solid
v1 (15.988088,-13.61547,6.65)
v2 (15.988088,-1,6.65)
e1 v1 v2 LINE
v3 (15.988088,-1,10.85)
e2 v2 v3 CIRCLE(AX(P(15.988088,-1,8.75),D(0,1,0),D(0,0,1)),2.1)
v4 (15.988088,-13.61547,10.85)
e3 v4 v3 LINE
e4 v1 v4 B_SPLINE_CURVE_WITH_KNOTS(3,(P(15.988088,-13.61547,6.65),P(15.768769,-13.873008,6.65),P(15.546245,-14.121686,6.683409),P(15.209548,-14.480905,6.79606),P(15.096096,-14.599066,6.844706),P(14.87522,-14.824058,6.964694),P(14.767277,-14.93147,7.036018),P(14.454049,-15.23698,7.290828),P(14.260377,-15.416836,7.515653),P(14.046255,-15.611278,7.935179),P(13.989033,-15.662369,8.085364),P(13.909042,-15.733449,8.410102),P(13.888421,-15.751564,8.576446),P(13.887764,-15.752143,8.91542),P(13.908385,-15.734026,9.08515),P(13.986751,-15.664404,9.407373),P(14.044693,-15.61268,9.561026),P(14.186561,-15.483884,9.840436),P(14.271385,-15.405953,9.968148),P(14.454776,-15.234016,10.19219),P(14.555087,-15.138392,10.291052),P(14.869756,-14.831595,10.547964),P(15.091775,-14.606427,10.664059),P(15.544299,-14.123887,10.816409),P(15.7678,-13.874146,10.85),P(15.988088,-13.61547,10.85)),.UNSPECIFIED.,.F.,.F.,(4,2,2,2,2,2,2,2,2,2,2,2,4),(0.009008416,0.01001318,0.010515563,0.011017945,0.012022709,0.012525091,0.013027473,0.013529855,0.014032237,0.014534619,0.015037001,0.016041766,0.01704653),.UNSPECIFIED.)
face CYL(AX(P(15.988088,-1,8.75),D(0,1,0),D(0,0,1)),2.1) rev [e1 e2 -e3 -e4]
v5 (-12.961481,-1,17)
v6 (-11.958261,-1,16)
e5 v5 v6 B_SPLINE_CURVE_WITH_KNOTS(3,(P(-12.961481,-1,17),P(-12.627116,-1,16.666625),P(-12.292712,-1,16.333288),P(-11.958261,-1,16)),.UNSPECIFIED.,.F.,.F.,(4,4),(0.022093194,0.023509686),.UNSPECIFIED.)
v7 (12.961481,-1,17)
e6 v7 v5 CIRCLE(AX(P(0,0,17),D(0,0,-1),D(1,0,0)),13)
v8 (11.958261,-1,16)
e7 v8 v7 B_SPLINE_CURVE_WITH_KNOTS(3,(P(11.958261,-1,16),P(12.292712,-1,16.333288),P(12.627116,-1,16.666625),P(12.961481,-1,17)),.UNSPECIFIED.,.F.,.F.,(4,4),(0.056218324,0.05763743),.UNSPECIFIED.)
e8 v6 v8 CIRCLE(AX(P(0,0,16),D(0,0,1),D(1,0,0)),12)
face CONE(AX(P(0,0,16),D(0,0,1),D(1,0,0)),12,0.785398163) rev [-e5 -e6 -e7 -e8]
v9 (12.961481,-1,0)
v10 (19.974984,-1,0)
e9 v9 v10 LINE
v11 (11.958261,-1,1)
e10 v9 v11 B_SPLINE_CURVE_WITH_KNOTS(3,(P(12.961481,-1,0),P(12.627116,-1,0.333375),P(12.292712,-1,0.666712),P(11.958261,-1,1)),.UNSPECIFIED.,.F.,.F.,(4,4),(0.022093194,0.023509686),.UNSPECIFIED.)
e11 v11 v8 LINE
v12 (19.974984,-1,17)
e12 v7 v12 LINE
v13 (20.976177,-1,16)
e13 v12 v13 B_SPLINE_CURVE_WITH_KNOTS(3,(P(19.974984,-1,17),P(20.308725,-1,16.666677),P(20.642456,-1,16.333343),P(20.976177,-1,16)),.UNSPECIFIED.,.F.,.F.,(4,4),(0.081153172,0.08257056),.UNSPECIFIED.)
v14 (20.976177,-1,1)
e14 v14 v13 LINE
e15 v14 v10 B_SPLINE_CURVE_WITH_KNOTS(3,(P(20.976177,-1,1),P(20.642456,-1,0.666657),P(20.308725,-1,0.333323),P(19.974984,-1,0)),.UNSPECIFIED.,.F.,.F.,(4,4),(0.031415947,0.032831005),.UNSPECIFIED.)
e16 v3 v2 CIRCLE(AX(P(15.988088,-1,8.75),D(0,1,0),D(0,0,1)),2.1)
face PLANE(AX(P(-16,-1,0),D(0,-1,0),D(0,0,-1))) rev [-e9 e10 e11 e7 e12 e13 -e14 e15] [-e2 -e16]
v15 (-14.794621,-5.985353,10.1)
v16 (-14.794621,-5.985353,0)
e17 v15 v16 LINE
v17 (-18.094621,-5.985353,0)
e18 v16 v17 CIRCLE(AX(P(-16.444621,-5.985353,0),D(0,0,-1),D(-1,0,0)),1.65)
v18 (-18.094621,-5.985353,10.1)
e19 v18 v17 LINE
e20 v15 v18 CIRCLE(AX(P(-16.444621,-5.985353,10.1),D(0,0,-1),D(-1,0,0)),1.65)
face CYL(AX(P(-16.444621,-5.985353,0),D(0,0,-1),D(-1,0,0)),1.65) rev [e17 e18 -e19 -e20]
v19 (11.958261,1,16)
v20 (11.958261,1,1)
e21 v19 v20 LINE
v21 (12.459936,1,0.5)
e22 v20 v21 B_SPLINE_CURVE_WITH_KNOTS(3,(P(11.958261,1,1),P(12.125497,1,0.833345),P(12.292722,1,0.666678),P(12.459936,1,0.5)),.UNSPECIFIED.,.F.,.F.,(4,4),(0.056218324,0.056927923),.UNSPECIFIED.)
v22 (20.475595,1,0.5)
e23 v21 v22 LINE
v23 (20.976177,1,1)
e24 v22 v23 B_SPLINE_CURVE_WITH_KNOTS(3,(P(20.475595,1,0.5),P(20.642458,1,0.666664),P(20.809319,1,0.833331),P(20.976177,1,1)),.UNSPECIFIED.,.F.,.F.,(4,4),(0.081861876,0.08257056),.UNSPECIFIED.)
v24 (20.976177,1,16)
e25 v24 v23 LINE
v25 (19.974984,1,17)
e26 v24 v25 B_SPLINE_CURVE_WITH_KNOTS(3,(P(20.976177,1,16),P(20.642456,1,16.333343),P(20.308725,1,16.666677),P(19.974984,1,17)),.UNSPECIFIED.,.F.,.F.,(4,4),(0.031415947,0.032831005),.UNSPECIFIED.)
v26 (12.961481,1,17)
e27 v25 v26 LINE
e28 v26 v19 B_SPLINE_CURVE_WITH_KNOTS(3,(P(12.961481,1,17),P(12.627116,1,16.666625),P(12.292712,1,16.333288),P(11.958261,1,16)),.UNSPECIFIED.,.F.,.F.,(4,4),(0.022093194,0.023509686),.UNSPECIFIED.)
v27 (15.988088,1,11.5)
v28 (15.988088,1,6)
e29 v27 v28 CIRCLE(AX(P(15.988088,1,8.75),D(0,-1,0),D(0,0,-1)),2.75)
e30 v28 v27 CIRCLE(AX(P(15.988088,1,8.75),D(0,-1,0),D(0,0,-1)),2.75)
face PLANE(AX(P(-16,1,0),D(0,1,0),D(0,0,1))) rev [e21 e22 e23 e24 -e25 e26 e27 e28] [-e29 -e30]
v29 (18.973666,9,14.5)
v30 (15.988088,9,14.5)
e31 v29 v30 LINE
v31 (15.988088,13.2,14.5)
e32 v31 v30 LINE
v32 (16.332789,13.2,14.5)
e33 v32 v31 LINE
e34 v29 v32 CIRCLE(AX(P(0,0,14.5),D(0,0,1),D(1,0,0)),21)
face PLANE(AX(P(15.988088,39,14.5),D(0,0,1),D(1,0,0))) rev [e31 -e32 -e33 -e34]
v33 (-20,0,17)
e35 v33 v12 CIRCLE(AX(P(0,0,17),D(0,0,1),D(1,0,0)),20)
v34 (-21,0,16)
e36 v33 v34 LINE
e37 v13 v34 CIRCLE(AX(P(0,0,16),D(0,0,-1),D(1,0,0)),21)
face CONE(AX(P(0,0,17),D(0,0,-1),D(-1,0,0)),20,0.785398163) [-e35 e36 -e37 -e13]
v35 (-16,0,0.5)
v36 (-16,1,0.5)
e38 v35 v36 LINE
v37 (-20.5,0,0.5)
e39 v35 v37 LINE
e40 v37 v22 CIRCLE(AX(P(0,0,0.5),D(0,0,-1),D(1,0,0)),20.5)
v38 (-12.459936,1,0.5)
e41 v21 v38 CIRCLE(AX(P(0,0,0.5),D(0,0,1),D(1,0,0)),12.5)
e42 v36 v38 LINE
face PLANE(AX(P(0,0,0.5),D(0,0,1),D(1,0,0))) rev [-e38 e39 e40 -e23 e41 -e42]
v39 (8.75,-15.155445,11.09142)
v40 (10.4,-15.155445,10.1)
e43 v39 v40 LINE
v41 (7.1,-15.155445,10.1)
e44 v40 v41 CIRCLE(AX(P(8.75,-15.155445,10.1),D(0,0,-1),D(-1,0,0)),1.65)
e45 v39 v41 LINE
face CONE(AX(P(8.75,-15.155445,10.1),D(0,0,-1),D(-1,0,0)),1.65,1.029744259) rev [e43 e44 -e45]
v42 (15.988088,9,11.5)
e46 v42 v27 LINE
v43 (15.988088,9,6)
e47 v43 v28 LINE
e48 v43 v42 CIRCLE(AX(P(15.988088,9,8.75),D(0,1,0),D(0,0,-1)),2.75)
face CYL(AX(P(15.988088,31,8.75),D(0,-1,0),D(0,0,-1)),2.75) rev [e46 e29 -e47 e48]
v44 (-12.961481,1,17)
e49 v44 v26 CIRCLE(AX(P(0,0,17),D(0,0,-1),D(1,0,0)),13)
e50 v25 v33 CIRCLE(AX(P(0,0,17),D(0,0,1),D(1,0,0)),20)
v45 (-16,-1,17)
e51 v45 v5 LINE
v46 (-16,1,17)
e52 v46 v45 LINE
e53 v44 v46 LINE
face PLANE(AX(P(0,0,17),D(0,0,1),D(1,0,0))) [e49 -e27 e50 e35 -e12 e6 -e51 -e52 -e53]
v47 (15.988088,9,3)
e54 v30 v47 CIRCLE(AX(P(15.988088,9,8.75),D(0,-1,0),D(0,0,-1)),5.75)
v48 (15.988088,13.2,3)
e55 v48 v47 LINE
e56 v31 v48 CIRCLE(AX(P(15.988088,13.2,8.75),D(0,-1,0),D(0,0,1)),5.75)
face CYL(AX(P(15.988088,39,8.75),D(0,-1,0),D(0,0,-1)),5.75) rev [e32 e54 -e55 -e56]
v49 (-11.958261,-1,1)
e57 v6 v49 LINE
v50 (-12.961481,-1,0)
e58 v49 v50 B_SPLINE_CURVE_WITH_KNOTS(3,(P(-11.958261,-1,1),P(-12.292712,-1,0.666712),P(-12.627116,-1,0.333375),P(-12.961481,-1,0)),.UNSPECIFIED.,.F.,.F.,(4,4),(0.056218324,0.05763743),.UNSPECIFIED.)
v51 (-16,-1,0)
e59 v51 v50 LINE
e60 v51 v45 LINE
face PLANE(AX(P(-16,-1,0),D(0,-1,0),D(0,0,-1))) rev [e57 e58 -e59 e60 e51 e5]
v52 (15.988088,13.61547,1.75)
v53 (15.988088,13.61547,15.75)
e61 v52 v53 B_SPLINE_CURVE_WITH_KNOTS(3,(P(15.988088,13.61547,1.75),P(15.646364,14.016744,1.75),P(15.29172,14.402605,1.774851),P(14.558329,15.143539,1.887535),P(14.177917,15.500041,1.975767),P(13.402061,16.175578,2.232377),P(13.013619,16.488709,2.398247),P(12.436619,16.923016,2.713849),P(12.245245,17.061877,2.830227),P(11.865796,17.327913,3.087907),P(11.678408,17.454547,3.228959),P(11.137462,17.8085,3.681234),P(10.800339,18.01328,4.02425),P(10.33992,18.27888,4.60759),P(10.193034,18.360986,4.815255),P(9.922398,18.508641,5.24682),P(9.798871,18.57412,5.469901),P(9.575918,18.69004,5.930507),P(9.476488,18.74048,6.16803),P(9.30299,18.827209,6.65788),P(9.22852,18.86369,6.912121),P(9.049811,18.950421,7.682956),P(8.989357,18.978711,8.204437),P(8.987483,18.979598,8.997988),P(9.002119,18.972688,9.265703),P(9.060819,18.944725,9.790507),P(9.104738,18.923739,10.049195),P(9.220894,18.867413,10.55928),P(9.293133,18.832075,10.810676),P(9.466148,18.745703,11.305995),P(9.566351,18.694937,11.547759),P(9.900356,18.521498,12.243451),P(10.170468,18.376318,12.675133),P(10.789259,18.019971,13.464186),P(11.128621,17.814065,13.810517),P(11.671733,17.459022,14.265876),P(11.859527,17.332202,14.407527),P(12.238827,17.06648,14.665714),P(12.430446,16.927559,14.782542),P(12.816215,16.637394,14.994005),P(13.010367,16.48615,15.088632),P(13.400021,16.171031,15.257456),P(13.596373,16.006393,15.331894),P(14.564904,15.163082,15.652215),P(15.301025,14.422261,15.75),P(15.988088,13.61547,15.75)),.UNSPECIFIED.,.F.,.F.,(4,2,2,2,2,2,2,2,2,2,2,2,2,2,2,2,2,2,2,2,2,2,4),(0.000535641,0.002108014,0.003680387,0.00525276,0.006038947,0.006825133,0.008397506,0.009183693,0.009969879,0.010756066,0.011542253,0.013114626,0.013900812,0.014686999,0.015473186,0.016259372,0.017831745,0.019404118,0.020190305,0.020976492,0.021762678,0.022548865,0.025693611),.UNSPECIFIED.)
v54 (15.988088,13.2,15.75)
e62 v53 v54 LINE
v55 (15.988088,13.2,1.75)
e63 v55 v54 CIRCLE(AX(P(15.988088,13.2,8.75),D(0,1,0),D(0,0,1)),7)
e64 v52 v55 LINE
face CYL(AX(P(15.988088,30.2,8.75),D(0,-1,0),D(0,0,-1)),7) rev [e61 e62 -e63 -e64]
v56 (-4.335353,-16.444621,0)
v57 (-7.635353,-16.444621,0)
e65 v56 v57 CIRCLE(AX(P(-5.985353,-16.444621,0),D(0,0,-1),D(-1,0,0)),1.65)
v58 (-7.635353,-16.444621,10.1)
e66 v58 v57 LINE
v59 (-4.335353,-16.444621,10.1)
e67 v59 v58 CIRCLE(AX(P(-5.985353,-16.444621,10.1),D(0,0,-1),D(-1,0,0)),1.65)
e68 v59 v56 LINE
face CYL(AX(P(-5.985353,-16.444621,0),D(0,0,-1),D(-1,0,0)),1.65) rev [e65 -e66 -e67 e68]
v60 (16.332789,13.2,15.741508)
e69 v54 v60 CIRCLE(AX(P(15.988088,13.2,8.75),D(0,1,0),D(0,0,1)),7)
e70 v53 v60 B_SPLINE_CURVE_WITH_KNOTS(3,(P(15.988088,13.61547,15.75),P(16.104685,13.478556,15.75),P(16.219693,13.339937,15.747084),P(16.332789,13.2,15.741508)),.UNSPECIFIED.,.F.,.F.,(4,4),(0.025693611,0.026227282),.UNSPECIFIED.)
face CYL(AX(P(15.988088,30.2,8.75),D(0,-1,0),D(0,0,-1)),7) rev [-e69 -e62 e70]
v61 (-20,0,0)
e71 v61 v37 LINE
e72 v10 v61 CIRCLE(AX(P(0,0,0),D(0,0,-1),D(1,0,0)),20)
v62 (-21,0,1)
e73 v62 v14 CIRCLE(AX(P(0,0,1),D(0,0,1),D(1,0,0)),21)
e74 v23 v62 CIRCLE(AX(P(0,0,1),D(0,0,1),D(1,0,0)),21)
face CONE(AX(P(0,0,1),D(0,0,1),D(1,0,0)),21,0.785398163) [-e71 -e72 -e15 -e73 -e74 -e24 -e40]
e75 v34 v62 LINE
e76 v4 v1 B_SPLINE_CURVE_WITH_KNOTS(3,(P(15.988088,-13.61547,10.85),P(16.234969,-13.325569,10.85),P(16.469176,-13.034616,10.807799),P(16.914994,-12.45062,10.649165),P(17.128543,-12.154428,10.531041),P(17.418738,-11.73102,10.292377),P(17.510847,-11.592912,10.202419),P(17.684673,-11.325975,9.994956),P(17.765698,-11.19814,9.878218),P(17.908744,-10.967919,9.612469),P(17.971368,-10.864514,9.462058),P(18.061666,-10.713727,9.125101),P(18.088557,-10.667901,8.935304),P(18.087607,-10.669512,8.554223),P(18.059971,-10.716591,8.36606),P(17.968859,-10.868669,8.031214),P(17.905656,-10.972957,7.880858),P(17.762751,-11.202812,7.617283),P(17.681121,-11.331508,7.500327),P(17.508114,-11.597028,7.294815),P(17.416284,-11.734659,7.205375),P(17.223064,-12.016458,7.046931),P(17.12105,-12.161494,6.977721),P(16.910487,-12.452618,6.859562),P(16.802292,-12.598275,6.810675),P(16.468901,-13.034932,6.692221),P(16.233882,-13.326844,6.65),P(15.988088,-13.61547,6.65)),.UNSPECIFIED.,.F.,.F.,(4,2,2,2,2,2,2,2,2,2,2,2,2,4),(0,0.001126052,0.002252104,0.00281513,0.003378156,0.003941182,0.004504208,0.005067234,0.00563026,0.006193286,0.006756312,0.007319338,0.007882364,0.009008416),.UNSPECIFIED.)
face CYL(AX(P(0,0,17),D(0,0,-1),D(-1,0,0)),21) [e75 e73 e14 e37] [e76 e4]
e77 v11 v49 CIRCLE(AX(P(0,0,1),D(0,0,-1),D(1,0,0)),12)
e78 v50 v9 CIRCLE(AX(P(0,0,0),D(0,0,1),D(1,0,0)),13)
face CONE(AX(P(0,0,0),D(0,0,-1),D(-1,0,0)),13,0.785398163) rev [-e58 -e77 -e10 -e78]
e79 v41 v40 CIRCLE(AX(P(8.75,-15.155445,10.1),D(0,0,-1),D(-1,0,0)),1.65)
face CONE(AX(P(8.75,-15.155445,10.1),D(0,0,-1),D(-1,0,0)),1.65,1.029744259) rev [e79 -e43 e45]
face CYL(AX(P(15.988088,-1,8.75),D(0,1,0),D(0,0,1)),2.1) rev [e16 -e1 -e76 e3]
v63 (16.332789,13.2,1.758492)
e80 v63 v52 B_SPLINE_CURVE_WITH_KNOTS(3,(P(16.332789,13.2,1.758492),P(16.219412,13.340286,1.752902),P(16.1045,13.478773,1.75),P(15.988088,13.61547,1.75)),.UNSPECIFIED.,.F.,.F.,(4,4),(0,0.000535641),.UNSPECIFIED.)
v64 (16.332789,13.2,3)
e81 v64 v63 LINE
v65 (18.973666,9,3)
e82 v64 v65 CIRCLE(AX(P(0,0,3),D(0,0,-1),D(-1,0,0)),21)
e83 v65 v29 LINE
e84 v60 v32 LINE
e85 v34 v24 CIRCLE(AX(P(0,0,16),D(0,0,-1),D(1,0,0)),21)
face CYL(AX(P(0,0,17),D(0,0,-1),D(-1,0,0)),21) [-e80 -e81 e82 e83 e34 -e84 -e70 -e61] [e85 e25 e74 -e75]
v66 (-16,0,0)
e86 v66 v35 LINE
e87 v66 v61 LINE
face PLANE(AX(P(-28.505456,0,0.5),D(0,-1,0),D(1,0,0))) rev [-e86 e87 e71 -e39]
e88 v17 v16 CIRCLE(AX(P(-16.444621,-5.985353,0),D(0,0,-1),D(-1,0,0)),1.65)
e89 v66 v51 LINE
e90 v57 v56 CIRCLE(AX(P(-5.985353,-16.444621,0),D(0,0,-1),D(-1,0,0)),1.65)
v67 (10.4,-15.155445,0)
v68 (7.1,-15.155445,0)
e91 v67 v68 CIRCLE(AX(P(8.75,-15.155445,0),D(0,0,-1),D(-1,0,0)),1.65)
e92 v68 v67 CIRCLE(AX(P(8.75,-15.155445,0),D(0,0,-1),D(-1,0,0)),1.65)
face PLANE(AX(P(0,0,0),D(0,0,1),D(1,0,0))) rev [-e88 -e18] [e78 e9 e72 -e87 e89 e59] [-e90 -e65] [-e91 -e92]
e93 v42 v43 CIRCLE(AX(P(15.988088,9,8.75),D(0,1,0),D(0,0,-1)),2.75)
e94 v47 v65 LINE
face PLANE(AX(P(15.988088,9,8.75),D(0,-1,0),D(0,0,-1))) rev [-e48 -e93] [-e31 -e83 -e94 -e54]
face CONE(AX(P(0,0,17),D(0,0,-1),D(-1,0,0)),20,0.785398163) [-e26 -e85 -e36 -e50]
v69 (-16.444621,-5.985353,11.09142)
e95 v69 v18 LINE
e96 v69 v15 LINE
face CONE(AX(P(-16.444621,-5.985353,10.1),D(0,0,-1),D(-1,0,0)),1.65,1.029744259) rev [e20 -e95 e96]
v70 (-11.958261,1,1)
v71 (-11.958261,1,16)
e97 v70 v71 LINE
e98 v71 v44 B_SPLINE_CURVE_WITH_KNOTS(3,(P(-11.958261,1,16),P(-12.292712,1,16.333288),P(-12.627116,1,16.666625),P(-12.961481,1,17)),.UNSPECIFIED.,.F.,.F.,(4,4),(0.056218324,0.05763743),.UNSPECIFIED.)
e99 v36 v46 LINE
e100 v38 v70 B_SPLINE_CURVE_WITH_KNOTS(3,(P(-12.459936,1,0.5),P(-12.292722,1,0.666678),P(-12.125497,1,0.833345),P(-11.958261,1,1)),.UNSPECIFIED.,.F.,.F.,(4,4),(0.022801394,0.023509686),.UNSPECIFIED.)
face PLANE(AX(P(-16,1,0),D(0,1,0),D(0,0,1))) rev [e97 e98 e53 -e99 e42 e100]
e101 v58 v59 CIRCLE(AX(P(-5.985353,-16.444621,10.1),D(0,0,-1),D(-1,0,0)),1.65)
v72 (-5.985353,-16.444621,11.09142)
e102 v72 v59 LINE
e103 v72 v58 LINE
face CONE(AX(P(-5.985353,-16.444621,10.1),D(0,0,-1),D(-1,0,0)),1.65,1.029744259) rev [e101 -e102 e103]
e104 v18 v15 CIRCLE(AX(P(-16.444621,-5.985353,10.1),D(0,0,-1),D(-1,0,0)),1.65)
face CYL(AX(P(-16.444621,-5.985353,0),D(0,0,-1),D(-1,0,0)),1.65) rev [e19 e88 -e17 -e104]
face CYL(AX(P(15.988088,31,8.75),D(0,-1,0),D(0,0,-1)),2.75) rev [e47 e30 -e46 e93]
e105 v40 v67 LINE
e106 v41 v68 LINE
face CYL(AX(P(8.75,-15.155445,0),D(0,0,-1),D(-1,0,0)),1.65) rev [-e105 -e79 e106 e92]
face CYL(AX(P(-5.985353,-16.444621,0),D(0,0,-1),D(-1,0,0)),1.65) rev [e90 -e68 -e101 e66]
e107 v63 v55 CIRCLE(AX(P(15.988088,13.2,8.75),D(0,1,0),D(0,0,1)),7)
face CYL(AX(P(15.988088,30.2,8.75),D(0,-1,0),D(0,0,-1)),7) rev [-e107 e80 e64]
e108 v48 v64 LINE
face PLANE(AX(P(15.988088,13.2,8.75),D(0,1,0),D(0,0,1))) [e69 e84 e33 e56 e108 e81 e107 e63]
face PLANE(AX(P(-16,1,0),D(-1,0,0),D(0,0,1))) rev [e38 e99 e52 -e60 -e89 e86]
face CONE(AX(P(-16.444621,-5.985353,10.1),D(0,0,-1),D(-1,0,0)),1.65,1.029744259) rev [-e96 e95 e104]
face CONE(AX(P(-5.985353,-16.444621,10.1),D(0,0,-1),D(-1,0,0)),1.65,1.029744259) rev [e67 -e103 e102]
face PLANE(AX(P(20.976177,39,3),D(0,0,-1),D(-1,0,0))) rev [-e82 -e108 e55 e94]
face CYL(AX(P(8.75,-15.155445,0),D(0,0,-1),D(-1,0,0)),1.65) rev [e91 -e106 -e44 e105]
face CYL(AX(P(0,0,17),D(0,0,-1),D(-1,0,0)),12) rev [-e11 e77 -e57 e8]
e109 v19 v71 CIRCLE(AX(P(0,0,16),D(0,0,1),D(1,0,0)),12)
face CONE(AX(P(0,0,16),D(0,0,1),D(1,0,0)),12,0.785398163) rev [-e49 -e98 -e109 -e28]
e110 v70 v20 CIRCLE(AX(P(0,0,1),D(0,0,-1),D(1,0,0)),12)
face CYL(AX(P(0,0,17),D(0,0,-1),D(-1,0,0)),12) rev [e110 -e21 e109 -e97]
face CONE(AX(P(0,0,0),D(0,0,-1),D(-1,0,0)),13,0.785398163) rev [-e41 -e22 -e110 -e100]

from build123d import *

# Parameters (mm, degrees)
SKETCH2_R             = 21
SKETCH2_R_2           = 12
BOSS_EXTRUDE2_DEPTH   = 17
CHAMFER1_SIZE         = 1
SKETCH3_W             = 46.185652856
SKETCH3_H             = 2
CUT_EXTRUDE1_DEPTH    = 35.219877265
SKETCH5_R             = 2.75
CUT_EXTRUDE3_DEPTH    = 30
CUT_EXTRUDE4_START    = -8
CUT_EXTRUDE4_DEPTH    = 30
M5_TAPPED_HOLE1_D     = 4.2
SKETCH9_W             = 59.171214414
SKETCH9_H             = 29.501144874
CUT_EXTRUDE5_DEPTH    = 0.5
M4_TAPPED_HOLE1_D     = 3.3
M4_TAPPED_HOLE1_DEPTH = 10.1
M4_TAPPED_HOLE1_TIP   = 0.991420021
SKETCH13_R            = 7
CUT_EXTRUDE7_DEPTH    = 17


with BuildPart() as part:
    # Sketch2 → Boss-Extrude2 (new body)
    with BuildSketch(Plane.XY):
        Circle(SKETCH2_R)
        Circle(SKETCH2_R_2, mode=Mode.SUBTRACT)
    extrude(amount=BOSS_EXTRUDE2_DEPTH)

    # Chamfer1
    chamfer1_edges = [part.edges().sort_by_distance(p)[0] for p in [
        (-21, 0, 0),
        (-21, 0, 17),
        (-12, 0, 0),
        (-12, 0, 17),
    ]]
    chamfer(chamfer1_edges, length=CHAMFER1_SIZE)

    # Sketch3 → Cut-Extrude1 (cut, through all)
    with BuildSketch(Plane.XY.offset(17)):
        with Locations((7.092826428, 0)):
            Rectangle(SKETCH3_W, SKETCH3_H)
    extrude(amount=-CUT_EXTRUDE1_DEPTH, mode=Mode.SUBTRACT)

    # Sketch5 → Cut-Extrude3 (cut)
    with BuildSketch(Plane.XZ.offset(-1)):
        with Locations(Location((15.988088482, 8.75, 0), (0, 0, 270))):
            Circle(SKETCH5_R)
    extrude(amount=-CUT_EXTRUDE3_DEPTH, mode=Mode.SUBTRACT)

    # Sketch6 → Cut-Extrude4 (cut)
    with BuildSketch(Plane.XZ.offset(-1).offset(CUT_EXTRUDE4_START)):
        with BuildLine():
            Line((15.988088482, 14.5), (20.976176963, 14.5))
            Line((20.976176963, 14.5), (20.976176963, 3))
            Line((20.976176963, 3), (15.988088482, 3))
            ThreePointArc((15.988088482, 3), (10.238088482, 8.75), (15.988088482, 14.5))
        make_face()
    extrude(amount=-CUT_EXTRUDE4_DEPTH, mode=Mode.SUBTRACT)

    # M5 Tapped Hole1 (through all)
    with Locations(Plane(origin=(0, -1, 0), x_dir=(1, 0, 0), z_dir=(0, 1, 0))):
        with Locations((15.988088482, -8.75)):
            Hole(M5_TAPPED_HOLE1_D / 2)

    # Sketch9 → Cut-Extrude5 (cut)
    with BuildSketch(Plane(origin=(0, 0, 0), x_dir=(-1, 0, 0), z_dir=(0, 0, -1))):
        with Locations((-1.080150951, 14.750572437)):
            Rectangle(SKETCH9_W, SKETCH9_H)
    extrude(amount=-CUT_EXTRUDE5_DEPTH, mode=Mode.SUBTRACT)

    # M4 Tapped Hole1
    with Locations(Plane(origin=(0, 0, 0), x_dir=(-1, 0, 0), z_dir=(0, 0, -1))):
        with Locations((16.444620864, -5.985352508), (-8.75, -15.155444566), (5.985352508, -16.444620864)):
            Hole(M4_TAPPED_HOLE1_D / 2, depth=M4_TAPPED_HOLE1_DEPTH)
            with Locations((0, 0, -(M4_TAPPED_HOLE1_DEPTH + M4_TAPPED_HOLE1_TIP / 2))):  # 118° drill point
                Cone(0, M4_TAPPED_HOLE1_D / 2, M4_TAPPED_HOLE1_TIP, mode=Mode.SUBTRACT)

    # Sketch13 → Cut-Extrude7 (cut)
    with BuildSketch(Plane(origin=(0, 13.2, 0), x_dir=(1, 0, 0), z_dir=(0, 1, 0))):
        with Locations((15.988088482, -8.75)):
            Circle(SKETCH13_R)
    extrude(amount=CUT_EXTRUDE7_DEPTH, mode=Mode.SUBTRACT)


solid = part.part
